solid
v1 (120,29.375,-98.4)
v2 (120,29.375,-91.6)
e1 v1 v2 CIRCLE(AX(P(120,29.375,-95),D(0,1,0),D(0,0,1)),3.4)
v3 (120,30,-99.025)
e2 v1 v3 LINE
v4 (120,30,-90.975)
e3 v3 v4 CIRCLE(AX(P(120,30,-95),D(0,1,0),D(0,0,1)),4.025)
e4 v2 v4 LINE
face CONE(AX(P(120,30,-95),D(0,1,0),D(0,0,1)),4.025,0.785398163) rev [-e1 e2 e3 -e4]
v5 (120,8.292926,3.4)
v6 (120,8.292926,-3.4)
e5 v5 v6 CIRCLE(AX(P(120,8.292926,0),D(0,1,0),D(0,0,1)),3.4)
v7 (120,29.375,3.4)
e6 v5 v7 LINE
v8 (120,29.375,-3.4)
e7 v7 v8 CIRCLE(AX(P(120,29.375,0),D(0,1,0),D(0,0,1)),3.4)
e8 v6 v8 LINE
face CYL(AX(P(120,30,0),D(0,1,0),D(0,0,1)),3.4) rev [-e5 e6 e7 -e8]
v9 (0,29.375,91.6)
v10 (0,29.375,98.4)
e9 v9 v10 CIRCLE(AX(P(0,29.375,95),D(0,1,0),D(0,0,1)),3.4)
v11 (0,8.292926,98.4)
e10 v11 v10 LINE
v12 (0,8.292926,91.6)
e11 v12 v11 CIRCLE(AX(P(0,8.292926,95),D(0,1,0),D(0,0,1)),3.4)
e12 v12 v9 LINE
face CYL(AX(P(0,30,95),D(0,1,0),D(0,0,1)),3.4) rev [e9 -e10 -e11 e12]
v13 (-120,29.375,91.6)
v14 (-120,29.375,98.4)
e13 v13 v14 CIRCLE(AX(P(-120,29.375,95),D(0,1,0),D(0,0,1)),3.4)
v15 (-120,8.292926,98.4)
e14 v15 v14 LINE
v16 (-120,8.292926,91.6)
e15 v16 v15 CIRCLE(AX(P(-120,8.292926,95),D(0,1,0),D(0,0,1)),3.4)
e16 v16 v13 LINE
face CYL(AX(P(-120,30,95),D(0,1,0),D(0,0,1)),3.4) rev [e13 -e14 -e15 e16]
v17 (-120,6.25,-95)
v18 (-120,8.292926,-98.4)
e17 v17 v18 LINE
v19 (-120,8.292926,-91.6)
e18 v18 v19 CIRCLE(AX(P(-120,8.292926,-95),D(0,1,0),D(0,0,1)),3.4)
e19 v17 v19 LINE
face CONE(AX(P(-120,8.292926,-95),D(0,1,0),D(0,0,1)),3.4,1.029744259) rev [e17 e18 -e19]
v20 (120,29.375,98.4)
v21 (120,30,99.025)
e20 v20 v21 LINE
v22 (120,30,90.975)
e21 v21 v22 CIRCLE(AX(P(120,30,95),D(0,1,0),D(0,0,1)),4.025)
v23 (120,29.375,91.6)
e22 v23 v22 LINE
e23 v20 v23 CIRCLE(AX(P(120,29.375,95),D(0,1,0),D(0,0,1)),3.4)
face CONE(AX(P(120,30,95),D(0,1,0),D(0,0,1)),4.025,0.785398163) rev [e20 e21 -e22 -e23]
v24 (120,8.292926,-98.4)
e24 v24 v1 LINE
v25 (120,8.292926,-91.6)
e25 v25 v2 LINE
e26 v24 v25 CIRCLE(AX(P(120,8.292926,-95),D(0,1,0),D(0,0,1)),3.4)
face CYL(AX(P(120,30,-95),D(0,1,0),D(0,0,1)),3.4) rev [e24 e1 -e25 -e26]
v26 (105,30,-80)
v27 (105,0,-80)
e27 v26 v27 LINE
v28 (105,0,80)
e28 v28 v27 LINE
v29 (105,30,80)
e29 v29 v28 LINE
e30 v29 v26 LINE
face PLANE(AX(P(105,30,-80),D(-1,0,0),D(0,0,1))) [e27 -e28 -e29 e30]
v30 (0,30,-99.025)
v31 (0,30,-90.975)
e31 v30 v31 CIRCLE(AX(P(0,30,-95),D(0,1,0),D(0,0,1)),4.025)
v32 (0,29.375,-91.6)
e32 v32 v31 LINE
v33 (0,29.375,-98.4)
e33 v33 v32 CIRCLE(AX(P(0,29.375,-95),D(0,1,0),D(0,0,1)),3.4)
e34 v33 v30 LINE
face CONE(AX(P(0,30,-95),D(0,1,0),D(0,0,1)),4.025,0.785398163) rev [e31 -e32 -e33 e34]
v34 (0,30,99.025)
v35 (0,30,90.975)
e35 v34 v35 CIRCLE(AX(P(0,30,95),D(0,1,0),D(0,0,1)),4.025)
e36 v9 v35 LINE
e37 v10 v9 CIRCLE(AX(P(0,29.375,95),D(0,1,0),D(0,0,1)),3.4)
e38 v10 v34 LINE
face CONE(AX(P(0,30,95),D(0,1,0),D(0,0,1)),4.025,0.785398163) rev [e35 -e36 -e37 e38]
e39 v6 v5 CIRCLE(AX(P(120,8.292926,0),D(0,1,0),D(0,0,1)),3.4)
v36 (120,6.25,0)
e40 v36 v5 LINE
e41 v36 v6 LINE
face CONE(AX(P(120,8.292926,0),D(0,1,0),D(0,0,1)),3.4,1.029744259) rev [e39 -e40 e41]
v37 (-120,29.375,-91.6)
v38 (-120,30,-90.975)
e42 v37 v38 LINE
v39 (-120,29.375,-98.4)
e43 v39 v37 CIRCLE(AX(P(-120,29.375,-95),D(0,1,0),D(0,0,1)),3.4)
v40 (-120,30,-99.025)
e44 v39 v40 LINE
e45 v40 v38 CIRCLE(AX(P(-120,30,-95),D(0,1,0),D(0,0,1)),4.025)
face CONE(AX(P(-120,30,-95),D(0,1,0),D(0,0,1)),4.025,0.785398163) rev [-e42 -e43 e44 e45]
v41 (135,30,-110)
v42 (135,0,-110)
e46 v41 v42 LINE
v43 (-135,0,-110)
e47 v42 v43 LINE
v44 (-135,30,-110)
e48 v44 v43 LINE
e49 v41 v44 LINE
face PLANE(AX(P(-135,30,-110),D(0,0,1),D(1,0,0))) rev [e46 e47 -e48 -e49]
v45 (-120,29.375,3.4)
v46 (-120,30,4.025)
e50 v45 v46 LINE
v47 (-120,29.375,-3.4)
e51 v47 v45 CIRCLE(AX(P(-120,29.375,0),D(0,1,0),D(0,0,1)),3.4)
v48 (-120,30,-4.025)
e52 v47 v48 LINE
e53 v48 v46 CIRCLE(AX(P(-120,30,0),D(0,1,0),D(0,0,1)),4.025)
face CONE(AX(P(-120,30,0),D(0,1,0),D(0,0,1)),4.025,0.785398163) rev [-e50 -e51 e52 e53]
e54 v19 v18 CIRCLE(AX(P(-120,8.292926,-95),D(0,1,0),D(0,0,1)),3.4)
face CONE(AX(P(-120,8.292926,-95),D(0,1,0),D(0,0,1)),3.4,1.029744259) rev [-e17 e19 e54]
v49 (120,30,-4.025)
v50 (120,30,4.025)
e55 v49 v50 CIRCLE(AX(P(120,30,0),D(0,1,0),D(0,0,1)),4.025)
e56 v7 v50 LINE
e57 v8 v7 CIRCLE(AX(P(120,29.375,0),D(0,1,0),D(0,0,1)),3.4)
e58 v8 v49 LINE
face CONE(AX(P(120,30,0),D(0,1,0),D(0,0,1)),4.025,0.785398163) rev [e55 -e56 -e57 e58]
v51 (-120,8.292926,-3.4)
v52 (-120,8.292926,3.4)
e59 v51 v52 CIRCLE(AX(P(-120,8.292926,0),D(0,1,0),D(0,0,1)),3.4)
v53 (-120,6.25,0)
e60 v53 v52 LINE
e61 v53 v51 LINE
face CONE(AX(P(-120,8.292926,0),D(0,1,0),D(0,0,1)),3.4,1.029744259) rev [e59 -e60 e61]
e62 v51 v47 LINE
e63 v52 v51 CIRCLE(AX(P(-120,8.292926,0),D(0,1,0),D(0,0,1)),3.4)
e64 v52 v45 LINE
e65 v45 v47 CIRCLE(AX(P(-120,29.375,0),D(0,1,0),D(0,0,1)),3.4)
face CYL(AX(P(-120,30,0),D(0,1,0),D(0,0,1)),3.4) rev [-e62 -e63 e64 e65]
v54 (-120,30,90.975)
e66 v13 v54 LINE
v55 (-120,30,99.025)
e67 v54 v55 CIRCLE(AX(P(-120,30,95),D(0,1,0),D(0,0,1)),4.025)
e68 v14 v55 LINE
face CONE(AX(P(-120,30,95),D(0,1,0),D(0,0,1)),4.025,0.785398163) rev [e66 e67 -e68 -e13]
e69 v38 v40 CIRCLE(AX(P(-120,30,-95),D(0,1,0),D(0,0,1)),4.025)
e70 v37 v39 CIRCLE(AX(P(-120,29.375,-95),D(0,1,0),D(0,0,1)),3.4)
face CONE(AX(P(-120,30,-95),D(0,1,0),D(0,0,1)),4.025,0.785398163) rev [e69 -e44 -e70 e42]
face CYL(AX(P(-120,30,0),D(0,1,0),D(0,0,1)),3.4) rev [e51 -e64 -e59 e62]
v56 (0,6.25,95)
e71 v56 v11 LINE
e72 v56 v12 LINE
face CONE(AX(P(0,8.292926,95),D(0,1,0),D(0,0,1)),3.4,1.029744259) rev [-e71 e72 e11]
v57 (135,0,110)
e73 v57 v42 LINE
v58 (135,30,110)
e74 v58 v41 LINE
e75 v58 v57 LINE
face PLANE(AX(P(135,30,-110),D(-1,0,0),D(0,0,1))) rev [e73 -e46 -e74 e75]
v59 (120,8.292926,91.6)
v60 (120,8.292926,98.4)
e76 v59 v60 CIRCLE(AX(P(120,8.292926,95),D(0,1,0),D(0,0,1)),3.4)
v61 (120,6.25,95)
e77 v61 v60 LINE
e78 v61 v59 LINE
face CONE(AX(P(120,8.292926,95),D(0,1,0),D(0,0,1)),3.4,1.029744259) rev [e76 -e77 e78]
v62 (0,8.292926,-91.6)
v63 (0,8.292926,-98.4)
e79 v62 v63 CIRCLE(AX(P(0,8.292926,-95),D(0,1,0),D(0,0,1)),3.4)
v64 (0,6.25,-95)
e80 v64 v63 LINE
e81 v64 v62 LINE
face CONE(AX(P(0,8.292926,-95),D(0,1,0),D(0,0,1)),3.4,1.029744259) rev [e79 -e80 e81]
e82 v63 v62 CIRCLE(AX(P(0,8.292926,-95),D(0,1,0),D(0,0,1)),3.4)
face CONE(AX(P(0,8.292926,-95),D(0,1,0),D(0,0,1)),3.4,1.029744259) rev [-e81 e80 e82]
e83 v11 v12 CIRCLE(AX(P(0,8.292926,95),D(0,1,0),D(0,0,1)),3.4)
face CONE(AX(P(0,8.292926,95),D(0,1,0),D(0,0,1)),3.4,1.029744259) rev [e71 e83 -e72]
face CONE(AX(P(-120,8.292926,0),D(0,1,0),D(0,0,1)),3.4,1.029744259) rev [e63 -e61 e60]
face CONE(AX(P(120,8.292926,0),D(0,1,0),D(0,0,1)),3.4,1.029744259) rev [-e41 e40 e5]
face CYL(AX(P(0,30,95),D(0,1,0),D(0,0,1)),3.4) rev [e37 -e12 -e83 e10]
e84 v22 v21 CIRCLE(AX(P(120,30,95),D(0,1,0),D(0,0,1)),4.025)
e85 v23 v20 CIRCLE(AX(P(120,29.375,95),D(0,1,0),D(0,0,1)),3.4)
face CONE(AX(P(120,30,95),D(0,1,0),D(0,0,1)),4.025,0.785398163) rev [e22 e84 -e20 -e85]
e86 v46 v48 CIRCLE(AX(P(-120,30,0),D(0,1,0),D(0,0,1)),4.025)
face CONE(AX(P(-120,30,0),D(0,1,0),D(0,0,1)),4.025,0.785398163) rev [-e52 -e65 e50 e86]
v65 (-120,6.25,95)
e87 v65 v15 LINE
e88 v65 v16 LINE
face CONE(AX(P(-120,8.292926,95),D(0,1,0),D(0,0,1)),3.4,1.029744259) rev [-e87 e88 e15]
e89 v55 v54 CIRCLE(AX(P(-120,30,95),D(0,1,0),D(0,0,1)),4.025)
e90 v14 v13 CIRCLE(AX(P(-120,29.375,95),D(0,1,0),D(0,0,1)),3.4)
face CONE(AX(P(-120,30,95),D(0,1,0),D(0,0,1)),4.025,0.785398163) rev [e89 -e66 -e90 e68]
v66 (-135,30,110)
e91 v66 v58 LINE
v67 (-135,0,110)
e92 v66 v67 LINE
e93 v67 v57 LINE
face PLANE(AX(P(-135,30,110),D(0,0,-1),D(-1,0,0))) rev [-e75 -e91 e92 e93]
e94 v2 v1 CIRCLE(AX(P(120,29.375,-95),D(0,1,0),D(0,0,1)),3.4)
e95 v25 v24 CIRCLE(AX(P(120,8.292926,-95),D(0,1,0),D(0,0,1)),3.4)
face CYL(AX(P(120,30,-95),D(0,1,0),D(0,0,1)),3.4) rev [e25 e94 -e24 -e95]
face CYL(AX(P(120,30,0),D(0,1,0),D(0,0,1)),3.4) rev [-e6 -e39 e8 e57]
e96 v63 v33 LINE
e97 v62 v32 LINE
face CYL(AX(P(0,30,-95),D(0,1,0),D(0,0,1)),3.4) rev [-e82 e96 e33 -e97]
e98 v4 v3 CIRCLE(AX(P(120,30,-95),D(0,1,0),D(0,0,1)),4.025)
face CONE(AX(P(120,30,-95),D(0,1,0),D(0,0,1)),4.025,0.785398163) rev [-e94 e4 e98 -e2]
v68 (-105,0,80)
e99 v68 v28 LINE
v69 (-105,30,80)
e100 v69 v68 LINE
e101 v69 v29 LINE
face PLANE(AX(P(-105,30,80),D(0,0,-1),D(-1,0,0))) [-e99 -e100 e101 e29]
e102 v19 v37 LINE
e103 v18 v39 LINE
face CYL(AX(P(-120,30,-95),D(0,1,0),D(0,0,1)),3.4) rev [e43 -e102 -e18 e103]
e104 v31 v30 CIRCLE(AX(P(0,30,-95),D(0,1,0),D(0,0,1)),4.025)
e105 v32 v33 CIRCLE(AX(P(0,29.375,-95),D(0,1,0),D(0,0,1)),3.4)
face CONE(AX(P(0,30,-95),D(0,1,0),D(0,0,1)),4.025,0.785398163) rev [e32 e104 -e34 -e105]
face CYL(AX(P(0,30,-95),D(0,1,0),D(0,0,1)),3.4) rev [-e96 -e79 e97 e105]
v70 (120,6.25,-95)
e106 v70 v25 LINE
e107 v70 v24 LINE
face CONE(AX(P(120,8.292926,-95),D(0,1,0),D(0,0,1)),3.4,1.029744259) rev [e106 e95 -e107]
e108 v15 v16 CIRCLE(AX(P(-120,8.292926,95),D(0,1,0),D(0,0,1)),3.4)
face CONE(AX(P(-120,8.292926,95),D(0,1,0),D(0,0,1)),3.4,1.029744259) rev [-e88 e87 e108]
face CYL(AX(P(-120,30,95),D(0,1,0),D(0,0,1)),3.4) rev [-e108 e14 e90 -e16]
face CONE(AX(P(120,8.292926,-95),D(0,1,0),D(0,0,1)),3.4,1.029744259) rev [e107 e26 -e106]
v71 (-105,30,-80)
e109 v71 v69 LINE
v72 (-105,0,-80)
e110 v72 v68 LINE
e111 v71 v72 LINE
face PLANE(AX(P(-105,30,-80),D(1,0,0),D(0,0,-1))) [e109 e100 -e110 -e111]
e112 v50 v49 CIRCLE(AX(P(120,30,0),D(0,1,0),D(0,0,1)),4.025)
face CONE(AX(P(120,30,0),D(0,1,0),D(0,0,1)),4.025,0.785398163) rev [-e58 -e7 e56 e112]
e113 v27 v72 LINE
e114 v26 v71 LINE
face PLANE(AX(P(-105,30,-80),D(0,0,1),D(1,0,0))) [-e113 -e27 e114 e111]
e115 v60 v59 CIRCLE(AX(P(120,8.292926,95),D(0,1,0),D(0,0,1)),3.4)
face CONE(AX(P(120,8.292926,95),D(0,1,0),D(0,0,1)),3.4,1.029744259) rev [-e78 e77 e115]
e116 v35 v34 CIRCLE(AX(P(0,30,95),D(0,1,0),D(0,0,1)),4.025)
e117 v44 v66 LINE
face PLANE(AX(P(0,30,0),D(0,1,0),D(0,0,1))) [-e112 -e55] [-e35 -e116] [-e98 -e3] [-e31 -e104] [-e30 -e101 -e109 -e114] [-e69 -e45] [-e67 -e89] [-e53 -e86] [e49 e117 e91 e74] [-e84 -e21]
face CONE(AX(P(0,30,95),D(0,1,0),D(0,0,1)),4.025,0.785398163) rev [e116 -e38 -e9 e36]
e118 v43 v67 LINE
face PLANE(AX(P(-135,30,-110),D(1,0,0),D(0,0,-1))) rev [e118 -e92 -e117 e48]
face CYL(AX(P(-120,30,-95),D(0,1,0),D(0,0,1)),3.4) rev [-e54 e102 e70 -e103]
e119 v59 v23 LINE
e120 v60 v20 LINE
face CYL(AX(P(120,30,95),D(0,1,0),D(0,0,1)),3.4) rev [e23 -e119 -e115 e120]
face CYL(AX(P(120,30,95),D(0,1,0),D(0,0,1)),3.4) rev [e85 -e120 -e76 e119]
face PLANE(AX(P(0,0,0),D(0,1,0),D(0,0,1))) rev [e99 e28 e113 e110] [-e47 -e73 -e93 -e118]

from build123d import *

# Parameters (mm, degrees)
SKETCH1_W                   = 270
SKETCH1_H                   = 220
SKETCH1_W_2                 = 210
SKETCH1_H_2                 = 160
BOSS_EXTRUDE1_DEPTH         = 30
M8_TAPPED_HOLE1_D           = 6.8
M8_TAPPED_HOLE1_DEPTH       = 21.707073895
M8_TAPPED_HOLE1_CSINK_D     = 8.05
M8_TAPPED_HOLE1_CSINK_ANGLE = 90
M8_TAPPED_HOLE1_TIP         = 2.042926105


with BuildPart() as part:
    # Sketch1 → Boss-Extrude1 (new body)
    with BuildSketch(Plane(origin=(0, 0, 0), x_dir=(1, 0, 0), z_dir=(0, 1, 0))):
        Rectangle(SKETCH1_W, SKETCH1_H)
        Rectangle(SKETCH1_W_2, SKETCH1_H_2, mode=Mode.SUBTRACT)
    extrude(amount=BOSS_EXTRUDE1_DEPTH)

    # M8 Tapped Hole1
    with Locations(Plane(origin=(0, 30, 0), x_dir=(1, 0, 0), z_dir=(0, 1, 0))):
        with Locations((0, 95), (-120, 95), (-120, 0), (-120, -95), (0, -95), (120, -95), (120, 95), (120, 0)):
            CounterSinkHole(M8_TAPPED_HOLE1_D / 2, M8_TAPPED_HOLE1_CSINK_D / 2, depth=M8_TAPPED_HOLE1_DEPTH, counter_sink_angle=M8_TAPPED_HOLE1_CSINK_ANGLE)
            with Locations((0, 0, -(M8_TAPPED_HOLE1_DEPTH + M8_TAPPED_HOLE1_TIP / 2))):  # 118° drill point
                Cone(0, M8_TAPPED_HOLE1_D / 2, M8_TAPPED_HOLE1_TIP, mode=Mode.SUBTRACT)


solid = part.part
